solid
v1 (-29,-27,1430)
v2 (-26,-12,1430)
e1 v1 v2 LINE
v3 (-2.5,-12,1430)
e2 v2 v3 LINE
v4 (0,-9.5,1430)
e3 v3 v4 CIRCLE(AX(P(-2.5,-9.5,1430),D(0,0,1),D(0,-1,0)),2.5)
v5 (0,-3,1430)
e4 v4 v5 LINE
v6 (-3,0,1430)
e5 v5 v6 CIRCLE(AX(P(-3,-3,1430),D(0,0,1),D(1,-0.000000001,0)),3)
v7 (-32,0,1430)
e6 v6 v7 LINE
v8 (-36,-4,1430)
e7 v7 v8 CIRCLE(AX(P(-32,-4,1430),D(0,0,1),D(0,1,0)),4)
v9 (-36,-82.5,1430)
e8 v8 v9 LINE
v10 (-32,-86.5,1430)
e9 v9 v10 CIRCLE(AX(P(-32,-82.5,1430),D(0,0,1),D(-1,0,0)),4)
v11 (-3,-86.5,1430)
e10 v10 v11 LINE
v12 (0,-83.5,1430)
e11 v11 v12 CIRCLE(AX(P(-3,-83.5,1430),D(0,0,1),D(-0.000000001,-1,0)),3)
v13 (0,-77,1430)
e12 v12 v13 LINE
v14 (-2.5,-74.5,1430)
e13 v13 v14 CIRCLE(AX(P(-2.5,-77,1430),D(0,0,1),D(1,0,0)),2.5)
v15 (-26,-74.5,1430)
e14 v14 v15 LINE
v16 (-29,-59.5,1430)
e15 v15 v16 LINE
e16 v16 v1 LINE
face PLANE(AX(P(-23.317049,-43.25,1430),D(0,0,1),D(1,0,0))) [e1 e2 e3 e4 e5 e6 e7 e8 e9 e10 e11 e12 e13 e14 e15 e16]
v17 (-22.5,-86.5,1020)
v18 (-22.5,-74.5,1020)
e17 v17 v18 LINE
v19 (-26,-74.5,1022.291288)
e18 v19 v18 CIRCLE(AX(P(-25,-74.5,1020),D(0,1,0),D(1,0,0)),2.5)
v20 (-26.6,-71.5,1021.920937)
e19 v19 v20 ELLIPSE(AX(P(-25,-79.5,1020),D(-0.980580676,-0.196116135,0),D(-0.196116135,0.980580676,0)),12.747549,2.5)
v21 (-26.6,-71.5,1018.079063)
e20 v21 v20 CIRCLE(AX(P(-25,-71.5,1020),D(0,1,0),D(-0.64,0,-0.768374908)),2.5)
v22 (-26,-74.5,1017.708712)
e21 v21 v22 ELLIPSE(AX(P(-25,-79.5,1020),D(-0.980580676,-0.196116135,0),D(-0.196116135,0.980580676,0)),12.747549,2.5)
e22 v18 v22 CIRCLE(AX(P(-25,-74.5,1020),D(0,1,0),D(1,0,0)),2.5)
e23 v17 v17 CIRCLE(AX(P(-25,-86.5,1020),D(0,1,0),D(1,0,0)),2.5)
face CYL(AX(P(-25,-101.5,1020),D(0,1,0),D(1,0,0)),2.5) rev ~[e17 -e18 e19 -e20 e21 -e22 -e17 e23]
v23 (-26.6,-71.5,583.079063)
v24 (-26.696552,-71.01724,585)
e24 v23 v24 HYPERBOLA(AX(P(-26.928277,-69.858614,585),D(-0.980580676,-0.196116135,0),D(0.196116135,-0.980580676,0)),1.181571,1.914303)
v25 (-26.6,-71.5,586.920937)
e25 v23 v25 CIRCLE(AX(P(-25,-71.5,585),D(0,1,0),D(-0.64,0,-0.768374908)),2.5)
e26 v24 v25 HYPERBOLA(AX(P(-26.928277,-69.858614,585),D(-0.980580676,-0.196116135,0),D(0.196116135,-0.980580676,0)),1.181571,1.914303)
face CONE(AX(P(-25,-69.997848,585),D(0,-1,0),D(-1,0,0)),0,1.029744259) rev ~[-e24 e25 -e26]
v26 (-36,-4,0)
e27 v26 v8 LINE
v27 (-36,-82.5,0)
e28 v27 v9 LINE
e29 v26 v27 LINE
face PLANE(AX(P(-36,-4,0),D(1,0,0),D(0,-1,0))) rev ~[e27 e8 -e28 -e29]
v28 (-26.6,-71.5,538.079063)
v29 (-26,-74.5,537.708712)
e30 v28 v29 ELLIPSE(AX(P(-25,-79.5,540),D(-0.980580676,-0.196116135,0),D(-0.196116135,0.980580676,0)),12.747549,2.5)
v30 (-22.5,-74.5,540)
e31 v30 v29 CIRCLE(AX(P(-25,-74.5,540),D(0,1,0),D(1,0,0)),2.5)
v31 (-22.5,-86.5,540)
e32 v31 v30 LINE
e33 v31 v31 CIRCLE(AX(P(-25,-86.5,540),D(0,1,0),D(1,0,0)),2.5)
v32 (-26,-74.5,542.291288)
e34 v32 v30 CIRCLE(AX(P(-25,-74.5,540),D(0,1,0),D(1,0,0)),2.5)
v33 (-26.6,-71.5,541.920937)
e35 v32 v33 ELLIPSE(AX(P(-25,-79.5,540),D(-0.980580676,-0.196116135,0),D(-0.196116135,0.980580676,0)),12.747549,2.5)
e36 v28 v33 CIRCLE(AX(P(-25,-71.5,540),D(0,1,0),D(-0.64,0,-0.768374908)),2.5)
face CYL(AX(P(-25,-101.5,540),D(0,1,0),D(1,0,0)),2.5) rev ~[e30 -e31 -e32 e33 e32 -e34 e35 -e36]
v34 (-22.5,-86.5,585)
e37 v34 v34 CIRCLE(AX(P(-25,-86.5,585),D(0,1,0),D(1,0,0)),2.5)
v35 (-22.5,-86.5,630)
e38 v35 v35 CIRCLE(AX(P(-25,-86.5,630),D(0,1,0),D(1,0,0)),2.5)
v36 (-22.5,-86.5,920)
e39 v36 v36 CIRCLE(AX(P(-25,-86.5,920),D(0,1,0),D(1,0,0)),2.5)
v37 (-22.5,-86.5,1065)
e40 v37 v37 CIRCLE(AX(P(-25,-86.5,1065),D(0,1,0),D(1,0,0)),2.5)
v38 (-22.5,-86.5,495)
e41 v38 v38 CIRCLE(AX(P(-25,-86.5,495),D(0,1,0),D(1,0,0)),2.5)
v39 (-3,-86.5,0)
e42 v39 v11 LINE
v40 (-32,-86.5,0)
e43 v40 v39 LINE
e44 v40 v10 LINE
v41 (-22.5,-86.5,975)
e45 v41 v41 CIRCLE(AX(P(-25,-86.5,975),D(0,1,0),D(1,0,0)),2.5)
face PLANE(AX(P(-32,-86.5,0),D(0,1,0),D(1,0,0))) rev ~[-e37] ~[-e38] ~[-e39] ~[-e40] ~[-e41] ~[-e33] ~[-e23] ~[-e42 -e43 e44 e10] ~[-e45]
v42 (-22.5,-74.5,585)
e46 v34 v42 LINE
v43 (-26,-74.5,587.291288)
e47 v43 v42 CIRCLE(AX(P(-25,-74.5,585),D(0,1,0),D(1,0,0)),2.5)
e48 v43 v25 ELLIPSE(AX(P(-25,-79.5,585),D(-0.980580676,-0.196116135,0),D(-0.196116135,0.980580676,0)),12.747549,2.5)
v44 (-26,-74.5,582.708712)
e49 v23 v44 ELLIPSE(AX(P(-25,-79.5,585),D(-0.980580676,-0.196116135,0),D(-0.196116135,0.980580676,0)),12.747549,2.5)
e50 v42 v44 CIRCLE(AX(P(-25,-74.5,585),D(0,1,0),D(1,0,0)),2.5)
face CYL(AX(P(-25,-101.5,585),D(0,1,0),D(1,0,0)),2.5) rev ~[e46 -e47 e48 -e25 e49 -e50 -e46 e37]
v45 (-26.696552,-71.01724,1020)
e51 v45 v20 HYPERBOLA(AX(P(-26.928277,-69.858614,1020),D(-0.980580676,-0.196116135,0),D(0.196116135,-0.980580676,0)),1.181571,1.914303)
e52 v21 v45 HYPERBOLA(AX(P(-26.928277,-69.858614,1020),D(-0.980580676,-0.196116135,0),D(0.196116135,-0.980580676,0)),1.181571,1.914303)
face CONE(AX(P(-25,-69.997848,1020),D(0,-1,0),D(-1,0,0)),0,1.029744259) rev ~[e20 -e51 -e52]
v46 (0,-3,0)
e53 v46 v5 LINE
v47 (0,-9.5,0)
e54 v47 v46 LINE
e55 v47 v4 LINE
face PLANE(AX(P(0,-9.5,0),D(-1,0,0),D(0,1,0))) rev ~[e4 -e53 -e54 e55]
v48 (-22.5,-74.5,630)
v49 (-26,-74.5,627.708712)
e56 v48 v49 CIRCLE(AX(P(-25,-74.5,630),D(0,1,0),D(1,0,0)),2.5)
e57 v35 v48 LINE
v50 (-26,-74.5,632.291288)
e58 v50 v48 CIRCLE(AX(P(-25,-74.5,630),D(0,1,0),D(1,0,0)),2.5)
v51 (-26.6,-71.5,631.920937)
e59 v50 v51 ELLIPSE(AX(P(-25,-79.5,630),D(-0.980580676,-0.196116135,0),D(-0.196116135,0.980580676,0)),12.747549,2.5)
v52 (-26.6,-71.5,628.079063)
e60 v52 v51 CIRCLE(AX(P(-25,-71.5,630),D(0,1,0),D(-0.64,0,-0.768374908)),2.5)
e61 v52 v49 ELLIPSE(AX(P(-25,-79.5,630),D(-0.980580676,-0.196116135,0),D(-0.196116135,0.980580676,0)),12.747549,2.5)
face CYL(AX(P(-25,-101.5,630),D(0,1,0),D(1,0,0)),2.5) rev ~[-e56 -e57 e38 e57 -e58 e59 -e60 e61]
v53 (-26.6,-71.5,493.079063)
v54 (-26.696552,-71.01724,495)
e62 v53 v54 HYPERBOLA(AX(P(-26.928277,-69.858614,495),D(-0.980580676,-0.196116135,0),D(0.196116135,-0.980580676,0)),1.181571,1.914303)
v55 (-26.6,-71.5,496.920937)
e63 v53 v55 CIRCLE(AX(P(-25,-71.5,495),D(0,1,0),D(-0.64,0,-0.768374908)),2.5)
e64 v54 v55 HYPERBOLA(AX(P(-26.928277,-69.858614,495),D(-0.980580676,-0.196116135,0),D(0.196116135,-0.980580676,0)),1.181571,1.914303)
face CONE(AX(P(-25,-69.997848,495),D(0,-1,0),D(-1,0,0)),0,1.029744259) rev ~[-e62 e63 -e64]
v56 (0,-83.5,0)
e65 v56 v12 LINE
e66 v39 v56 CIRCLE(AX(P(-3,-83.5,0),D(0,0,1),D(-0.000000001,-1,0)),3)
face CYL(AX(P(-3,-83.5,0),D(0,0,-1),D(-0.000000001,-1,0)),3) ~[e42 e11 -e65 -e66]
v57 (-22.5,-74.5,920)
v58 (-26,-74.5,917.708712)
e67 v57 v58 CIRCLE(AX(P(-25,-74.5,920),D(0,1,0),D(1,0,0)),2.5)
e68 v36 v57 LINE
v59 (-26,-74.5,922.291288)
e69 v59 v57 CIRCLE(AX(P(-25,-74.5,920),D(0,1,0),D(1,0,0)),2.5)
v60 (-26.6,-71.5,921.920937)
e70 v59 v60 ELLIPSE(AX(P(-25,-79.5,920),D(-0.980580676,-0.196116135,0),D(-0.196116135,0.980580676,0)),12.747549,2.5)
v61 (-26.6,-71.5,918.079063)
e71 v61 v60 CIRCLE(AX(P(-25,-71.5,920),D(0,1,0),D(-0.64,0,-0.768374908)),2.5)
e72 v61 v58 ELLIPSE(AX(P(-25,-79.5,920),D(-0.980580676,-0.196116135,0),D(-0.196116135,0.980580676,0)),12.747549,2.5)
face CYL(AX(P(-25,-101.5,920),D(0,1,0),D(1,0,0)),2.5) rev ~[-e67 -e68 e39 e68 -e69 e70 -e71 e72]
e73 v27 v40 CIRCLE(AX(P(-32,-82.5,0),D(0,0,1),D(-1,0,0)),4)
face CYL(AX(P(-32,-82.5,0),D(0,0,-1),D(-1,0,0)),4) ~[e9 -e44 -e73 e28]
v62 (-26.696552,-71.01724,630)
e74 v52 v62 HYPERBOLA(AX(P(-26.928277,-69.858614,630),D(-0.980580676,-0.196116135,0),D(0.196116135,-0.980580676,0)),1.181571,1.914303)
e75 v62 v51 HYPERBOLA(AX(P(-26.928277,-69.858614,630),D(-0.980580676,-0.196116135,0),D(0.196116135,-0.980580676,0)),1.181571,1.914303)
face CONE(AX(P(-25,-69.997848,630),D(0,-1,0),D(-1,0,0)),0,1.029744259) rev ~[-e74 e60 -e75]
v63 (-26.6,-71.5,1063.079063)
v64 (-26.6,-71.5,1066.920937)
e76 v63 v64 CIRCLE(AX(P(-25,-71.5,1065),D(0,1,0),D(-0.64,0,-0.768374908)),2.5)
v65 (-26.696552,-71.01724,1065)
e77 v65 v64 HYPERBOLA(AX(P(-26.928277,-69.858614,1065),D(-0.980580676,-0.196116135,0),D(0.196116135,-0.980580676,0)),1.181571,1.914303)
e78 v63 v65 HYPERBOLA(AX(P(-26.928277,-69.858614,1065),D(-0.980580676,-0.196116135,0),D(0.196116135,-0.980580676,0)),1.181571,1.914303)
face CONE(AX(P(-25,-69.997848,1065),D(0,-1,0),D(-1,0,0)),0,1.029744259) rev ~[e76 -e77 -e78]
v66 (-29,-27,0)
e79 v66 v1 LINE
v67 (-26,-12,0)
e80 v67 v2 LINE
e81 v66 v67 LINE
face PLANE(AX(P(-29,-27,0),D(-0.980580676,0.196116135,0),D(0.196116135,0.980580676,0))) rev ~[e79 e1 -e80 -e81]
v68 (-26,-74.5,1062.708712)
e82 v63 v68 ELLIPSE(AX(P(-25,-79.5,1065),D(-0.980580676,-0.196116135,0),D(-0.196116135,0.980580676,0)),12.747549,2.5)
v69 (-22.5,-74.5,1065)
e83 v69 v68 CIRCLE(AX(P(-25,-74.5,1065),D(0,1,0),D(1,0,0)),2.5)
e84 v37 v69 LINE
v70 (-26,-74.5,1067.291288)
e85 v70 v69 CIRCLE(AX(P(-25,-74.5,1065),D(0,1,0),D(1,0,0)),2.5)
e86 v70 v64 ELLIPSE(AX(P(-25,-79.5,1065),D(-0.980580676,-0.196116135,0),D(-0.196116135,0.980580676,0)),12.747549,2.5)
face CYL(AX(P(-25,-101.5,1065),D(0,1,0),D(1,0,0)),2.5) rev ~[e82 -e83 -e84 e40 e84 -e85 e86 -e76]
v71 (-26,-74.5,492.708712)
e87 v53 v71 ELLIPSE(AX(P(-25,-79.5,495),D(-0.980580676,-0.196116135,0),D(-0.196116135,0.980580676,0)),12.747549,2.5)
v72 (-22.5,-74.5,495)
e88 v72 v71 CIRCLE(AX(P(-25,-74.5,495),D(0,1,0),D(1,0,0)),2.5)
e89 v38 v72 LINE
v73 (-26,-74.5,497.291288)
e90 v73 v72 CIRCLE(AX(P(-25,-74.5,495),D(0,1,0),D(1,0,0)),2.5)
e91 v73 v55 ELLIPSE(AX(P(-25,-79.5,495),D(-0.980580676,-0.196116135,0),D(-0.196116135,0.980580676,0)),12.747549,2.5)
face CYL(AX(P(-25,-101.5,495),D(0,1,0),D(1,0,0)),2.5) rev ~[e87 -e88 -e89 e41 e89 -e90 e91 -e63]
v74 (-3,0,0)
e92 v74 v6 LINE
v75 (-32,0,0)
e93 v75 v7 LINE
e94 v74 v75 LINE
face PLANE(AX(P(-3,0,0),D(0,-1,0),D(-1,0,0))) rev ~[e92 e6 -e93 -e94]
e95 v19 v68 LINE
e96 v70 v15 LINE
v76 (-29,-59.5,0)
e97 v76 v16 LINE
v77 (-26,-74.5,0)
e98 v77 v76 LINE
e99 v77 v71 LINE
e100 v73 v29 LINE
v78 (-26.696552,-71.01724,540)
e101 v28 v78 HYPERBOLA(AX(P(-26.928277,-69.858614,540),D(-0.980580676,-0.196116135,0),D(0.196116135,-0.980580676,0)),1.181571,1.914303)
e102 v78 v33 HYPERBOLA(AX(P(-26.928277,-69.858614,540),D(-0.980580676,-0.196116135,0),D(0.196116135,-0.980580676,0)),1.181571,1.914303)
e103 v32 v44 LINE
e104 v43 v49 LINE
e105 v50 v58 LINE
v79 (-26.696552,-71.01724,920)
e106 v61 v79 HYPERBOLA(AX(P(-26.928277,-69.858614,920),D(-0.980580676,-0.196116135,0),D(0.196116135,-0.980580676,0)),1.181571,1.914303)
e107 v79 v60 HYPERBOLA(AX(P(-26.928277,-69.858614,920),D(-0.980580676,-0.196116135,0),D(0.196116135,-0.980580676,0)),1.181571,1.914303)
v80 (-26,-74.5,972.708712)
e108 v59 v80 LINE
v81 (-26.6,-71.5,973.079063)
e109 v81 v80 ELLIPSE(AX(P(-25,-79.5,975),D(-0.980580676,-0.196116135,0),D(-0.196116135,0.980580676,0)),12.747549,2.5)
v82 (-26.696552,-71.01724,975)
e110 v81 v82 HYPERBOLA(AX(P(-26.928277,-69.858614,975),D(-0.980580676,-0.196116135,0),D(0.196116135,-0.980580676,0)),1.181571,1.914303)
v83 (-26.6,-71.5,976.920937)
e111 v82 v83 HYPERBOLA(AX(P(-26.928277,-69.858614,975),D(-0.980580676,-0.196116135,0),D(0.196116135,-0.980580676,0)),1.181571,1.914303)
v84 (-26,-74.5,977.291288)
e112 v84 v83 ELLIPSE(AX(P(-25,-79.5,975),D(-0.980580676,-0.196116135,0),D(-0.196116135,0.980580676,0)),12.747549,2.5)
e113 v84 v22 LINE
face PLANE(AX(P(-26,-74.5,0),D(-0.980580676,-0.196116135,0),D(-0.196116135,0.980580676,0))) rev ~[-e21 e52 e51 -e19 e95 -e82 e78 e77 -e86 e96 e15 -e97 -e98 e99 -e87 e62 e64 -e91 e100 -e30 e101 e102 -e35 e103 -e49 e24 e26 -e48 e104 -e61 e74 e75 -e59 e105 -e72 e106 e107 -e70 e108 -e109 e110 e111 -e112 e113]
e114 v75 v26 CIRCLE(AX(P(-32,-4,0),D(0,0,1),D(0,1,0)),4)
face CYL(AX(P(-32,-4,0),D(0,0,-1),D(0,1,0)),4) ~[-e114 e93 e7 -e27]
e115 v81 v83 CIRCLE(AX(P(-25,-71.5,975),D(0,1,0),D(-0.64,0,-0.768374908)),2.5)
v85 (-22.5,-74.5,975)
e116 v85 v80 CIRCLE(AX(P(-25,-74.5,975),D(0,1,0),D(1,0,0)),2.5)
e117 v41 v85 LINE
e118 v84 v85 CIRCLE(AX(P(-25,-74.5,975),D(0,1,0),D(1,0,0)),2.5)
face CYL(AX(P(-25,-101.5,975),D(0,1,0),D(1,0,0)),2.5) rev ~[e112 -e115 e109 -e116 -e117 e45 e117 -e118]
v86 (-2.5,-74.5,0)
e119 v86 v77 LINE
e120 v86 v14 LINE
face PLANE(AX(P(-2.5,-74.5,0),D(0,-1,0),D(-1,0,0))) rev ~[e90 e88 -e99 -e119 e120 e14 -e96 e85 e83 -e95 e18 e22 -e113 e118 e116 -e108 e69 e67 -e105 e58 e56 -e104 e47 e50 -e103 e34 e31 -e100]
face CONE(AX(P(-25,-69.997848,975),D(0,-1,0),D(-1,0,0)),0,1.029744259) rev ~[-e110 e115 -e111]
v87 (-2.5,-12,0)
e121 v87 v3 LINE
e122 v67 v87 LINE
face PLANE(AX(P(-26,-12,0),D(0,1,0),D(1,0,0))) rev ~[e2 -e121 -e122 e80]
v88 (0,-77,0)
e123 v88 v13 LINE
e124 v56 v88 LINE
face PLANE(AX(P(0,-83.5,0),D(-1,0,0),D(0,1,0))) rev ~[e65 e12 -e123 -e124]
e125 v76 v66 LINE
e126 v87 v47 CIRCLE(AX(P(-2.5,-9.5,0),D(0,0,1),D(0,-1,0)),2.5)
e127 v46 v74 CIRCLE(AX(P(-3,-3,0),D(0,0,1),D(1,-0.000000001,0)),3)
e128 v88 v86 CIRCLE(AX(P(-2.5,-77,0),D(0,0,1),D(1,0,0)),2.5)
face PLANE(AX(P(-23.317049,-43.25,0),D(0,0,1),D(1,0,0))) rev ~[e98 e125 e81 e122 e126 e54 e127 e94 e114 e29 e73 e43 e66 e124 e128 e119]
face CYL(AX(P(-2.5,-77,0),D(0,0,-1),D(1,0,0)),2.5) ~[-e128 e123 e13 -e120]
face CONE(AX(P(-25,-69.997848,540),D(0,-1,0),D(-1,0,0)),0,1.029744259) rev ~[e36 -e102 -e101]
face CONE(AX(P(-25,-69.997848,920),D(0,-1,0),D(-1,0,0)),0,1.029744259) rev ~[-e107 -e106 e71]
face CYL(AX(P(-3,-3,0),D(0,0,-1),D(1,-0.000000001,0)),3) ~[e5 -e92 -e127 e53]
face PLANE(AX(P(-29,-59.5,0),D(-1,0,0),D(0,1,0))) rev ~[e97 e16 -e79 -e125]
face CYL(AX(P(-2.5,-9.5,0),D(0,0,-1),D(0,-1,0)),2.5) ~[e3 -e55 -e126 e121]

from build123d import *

# Parameters (mm, degrees)
BOSS_EXTRUDE1_DEPTH   = 1430
SKETCH2_R             = 2
CUT_EXTRUDE1_DEPTH    = 10
M6_TAPPED_HOLE1_D     = 5
M6_TAPPED_HOLE1_DEPTH = 15
M6_TAPPED_HOLE1_TIP   = 1.502151548


with BuildPart() as part:
    # Sketch1 → Boss-Extrude1 (new body)
    with BuildSketch(Plane.XY):
        with BuildLine():
            Line((-3, 0), (-32, 0))
            ThreePointArc((-32, 0), (-34.828427125, -1.171572875), (-36, -4))
            Line((-36, -4), (-36, -82.5))
            ThreePointArc((-36, -82.5), (-34.828427125, -85.328427125), (-32, -86.5))
            Line((-32, -86.5), (-3, -86.5))
            ThreePointArc((-3, -86.5), (-0.878679656, -85.621320344), (0, -83.5))
            Line((0, -83.5), (0, -77))
            ThreePointArc((0, -77), (-0.732233047, -75.232233047), (-2.5, -74.5))
            Line((-2.5, -74.5), (-26, -74.5))
            Line((-26, -74.5), (-29, -59.5))
            Line((-29, -59.5), (-29, -27))
            Line((-29, -27), (-26, -12))
            Line((-26, -12), (-2.5, -12))
            ThreePointArc((-2.5, -12), (-0.732233047, -11.267766953), (0, -9.5))
            Line((0, -9.5), (0, -3))
            ThreePointArc((0, -3), (-0.878679656, -0.878679656), (-3, 0))
        make_face()
    extrude(amount=BOSS_EXTRUDE1_DEPTH)

    # Sketch2 → Cut-Extrude1 (cut)
    with BuildSketch(Plane.XZ.offset(86.5)):
        with Locations(Location((-25, 495, 0), (0, 0, 270))):
            Circle(SKETCH2_R)
        with Locations(Location((-25, 540, 0), (0, 0, 270))):
            Circle(SKETCH2_R)
        with Locations(Location((-25, 975, 0), (0, 0, 270))):
            Circle(SKETCH2_R)
        with Locations(Location((-25, 585, 0), (0, 0, 270))):
            Circle(SKETCH2_R)
        with Locations(Location((-25, 630, 0), (0, 0, 270))):
            Circle(SKETCH2_R)
        with Locations(Location((-25, 1065, 0), (0, 0, 270))):
            Circle(SKETCH2_R)
        with Locations(Location((-25, 920, 0), (0, 0, 270))):
            Circle(SKETCH2_R)
        with Locations(Location((-25, 1020, 0), (0, 0, 270))):
            Circle(SKETCH2_R)
    extrude(amount=-CUT_EXTRUDE1_DEPTH, mode=Mode.SUBTRACT)

    # M6 Tapped Hole1
    with Locations(Plane(origin=(0, -86.5, 0), x_dir=(-1, 0, 0), z_dir=(0, -1, 0))):
        with Locations((25, -630), (25, -585), (25, -540), (25, -495), (25, -920), (25, -975), (25, -1020), (25, -1065)):
            Hole(M6_TAPPED_HOLE1_D / 2, depth=M6_TAPPED_HOLE1_DEPTH)
            with Locations((0, 0, -(M6_TAPPED_HOLE1_DEPTH + M6_TAPPED_HOLE1_TIP / 2))):  # 118° drill point
                Cone(0, M6_TAPPED_HOLE1_D / 2, M6_TAPPED_HOLE1_TIP, mode=Mode.SUBTRACT)


solid = part.part
